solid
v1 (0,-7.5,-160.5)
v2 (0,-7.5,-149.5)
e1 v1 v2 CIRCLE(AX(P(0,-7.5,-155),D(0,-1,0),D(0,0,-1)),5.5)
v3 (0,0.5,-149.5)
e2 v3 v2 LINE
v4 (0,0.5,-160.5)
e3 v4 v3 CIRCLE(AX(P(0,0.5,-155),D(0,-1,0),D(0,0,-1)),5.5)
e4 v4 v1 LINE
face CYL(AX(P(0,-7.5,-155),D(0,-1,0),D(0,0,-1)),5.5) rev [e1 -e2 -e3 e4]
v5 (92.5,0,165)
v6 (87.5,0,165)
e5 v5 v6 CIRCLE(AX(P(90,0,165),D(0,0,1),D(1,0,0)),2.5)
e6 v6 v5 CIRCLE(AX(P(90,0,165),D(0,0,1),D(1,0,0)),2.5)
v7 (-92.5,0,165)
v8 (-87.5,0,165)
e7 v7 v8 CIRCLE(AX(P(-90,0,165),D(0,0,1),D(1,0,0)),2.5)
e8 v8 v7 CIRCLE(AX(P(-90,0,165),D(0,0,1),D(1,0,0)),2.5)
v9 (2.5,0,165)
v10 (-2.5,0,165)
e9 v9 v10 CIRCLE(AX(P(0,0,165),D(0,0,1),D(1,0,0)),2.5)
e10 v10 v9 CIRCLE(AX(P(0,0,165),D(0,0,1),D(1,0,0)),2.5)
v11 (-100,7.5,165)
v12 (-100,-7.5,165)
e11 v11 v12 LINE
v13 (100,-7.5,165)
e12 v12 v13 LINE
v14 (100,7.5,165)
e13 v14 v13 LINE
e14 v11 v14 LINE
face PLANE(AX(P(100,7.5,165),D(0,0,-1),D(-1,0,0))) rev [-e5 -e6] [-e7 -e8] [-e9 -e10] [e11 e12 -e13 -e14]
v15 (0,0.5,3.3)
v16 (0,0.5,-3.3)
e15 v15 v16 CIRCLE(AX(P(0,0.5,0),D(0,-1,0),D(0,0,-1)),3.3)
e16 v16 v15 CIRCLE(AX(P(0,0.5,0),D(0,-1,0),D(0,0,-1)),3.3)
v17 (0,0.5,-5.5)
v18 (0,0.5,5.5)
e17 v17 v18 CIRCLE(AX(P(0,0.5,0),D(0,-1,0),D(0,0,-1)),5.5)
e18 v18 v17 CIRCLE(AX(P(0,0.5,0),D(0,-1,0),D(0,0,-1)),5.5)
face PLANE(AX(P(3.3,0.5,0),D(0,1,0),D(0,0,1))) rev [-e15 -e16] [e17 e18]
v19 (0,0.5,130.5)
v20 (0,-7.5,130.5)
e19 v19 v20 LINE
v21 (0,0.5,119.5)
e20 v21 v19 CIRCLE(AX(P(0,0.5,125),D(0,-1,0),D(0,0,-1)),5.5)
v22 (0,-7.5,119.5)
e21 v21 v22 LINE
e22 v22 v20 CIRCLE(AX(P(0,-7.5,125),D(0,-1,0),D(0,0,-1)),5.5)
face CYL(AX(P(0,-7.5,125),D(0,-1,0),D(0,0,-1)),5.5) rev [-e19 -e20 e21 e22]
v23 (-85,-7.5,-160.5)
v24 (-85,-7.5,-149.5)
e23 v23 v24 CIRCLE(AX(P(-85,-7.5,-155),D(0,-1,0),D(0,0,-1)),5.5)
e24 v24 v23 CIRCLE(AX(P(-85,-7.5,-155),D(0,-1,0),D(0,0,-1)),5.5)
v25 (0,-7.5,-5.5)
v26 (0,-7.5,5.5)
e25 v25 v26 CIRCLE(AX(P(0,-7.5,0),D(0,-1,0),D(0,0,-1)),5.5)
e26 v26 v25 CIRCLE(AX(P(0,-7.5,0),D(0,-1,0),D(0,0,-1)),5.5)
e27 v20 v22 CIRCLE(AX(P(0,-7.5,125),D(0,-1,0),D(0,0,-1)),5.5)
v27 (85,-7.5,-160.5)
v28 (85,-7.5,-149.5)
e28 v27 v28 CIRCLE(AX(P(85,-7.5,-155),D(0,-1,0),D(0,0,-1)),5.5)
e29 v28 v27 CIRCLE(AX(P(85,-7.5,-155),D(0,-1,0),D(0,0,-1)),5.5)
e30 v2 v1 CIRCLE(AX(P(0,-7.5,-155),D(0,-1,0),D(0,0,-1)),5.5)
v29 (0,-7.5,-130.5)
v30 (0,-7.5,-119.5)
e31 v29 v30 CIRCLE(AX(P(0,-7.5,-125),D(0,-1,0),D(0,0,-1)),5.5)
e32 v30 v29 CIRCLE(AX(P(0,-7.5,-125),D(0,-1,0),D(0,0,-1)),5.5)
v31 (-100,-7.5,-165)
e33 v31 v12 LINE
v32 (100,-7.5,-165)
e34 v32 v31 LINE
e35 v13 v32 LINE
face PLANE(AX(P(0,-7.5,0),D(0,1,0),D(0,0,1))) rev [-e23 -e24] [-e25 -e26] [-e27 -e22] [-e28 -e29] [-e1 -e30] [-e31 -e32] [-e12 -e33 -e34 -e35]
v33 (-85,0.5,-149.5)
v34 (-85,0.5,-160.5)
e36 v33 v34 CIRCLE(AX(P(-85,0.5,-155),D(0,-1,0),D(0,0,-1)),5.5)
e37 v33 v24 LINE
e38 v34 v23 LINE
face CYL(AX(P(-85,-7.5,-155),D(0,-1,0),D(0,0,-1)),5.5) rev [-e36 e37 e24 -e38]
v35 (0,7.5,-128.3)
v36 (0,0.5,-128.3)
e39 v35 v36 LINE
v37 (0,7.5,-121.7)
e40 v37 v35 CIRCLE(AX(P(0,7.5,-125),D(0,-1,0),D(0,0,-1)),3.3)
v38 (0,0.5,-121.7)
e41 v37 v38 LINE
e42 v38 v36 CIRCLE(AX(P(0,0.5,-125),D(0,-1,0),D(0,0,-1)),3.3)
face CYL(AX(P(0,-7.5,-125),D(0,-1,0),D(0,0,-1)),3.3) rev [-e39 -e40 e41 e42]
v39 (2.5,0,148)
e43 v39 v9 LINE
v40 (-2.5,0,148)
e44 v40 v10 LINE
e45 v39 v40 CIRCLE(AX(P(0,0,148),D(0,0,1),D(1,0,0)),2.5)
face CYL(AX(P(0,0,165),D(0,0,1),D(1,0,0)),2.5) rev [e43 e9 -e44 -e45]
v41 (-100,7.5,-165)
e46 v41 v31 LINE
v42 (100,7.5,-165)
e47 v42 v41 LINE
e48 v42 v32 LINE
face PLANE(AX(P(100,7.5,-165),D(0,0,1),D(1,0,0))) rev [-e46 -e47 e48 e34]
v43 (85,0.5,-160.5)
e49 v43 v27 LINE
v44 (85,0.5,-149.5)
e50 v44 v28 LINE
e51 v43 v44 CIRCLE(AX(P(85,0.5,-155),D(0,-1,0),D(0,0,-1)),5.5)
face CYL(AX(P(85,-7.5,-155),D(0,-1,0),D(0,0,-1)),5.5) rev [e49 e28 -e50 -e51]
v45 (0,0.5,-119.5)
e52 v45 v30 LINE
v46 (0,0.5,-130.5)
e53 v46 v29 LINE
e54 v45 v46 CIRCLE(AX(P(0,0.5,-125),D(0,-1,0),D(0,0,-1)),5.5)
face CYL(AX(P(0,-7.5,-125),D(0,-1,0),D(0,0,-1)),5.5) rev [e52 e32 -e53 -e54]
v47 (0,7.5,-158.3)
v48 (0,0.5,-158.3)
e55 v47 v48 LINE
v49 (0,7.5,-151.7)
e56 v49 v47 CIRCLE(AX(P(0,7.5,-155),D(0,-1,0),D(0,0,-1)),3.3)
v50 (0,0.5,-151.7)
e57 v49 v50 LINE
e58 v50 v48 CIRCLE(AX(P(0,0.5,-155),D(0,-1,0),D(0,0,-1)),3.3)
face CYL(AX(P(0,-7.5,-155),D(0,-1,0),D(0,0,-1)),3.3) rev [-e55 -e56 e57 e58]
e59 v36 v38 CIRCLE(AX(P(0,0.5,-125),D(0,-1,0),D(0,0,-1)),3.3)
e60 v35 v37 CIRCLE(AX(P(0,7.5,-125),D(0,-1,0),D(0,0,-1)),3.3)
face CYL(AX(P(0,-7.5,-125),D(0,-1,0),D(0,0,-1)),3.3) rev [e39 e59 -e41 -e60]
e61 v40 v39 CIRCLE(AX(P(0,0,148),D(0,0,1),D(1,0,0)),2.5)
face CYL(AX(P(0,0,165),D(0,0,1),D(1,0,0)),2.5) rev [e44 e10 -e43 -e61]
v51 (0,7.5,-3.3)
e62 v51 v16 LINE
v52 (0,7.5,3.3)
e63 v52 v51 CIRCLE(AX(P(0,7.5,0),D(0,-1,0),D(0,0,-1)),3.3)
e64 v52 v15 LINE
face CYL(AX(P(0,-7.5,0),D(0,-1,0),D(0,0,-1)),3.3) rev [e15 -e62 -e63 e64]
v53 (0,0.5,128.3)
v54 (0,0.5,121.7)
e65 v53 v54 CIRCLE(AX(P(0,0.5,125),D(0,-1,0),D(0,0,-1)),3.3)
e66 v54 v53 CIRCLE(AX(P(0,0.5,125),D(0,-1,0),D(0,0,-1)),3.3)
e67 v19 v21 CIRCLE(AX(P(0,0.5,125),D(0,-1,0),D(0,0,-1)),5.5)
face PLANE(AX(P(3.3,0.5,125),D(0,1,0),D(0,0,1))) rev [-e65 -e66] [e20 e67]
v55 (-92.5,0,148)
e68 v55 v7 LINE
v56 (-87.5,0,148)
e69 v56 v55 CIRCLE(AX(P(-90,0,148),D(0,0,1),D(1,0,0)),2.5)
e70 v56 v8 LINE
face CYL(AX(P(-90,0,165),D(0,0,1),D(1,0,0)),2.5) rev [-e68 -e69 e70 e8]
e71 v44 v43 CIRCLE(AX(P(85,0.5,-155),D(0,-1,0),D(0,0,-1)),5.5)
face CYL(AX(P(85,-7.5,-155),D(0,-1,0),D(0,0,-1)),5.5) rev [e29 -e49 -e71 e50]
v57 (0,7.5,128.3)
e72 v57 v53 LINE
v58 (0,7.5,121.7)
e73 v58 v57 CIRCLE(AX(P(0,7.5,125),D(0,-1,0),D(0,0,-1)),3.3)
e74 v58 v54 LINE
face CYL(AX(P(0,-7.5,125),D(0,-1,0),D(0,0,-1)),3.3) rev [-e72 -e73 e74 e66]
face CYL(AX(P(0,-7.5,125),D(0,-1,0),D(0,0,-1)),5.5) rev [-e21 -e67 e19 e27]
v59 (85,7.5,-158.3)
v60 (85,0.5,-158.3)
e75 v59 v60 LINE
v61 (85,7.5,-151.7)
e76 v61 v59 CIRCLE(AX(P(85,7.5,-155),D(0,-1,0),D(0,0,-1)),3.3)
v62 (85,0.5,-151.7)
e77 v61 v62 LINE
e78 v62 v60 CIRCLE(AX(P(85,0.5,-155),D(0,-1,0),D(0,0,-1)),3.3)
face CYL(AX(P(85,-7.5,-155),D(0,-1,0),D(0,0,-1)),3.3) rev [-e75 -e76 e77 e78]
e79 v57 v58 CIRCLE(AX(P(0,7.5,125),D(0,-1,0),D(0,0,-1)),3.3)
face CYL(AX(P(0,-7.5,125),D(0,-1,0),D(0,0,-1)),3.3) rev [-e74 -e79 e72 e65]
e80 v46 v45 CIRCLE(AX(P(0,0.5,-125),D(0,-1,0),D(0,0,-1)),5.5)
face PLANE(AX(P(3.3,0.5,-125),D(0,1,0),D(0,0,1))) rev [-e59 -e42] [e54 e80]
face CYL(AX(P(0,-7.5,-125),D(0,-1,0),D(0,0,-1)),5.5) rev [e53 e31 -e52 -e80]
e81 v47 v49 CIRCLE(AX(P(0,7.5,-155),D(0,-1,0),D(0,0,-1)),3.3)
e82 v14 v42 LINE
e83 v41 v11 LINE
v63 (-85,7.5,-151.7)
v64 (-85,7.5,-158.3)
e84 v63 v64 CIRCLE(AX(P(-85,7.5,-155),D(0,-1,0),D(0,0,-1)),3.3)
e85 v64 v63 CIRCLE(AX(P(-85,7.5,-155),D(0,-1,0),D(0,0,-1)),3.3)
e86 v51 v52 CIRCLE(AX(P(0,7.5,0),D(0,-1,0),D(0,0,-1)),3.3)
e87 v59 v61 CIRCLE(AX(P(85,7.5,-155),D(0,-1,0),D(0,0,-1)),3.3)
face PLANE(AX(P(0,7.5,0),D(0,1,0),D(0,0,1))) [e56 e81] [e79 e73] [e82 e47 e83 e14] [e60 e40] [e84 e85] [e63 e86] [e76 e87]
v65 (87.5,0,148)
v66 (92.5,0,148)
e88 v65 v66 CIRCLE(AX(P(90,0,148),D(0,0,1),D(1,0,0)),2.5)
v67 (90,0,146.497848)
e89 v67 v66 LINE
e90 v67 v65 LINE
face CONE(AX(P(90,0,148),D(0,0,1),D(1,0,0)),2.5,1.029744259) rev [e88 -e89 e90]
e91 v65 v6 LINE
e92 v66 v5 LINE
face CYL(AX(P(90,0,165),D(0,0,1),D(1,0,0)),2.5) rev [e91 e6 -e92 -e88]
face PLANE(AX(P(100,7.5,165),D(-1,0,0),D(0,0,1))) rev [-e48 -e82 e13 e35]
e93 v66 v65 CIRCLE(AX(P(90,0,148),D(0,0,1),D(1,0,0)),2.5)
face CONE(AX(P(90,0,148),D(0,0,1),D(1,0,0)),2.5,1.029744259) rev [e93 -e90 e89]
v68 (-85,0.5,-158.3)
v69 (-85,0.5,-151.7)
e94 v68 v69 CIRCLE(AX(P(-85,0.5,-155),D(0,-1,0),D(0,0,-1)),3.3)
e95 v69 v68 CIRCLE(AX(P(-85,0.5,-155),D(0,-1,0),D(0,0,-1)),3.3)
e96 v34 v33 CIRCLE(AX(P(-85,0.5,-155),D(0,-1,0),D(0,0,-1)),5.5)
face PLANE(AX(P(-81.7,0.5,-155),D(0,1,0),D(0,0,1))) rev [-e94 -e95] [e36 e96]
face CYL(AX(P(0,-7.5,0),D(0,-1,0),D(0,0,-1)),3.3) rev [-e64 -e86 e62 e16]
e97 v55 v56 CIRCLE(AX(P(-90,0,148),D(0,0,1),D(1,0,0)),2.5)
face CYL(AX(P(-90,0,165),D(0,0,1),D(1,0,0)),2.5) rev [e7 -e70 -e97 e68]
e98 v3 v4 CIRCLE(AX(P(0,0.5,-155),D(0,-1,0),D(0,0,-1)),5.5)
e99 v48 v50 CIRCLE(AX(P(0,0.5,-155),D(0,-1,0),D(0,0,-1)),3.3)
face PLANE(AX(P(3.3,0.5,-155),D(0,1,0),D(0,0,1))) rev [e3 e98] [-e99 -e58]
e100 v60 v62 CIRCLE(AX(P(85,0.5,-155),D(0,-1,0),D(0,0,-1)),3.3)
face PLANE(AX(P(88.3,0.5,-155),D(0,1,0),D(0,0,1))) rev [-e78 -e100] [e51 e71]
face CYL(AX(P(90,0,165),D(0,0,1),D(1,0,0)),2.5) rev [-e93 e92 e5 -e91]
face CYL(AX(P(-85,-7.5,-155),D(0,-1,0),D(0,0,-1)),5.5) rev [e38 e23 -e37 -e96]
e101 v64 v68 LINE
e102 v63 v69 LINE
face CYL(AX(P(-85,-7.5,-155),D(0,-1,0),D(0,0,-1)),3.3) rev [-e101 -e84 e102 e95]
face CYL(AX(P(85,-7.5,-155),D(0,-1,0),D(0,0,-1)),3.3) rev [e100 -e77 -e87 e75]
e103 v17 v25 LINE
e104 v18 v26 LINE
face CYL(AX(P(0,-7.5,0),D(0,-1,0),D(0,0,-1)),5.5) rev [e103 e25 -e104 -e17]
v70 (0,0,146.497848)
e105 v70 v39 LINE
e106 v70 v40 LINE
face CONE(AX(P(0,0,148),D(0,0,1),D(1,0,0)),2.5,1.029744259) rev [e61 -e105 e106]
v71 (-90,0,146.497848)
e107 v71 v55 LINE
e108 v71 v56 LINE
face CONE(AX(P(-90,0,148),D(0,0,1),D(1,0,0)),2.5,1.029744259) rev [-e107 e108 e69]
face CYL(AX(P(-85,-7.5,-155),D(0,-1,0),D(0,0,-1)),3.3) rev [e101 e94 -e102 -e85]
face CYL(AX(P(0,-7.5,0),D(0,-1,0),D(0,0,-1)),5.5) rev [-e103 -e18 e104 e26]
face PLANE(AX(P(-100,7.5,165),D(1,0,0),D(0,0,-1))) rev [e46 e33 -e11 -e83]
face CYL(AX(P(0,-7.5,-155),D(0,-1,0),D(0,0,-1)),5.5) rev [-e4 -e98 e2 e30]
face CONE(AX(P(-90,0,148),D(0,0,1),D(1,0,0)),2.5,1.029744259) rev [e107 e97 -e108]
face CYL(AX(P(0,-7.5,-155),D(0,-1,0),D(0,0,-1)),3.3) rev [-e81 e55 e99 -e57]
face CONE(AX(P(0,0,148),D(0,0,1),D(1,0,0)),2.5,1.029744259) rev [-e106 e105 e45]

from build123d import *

# Parameters (mm, degrees)
SKETCH_1_W                   = 200
SKETCH_1_H                   = 330
EXTRUDE_1_DEPTH              = 7.5
HOLE_WIZARD_M6_1_D           = 6.6
HOLE_WIZARD_M6_1_CBORE_D     = 11
HOLE_WIZARD_M6_1_CBORE_DEPTH = 8
HOLE_WIZARD_M6_2_D           = 6.6
HOLE_WIZARD_M6_2_CBORE_D     = 11
HOLE_WIZARD_M6_2_CBORE_DEPTH = 8
HOLE_WIZARD_M6_1_2_D         = 5
HOLE_WIZARD_M6_1_2_DEPTH     = 17
HOLE_WIZARD_M6_1_2_TIP       = 1.502151548


with BuildPart() as part:
    # 草图1 → 凸台-拉伸1 (new, symmetric)
    with BuildSketch(Plane(origin=(0, 0, 0), x_dir=(1, 0, 0), z_dir=(0, 1, 0))):
        Rectangle(SKETCH_1_W, SKETCH_1_H)
    extrude(amount=EXTRUDE_1_DEPTH, both=True)

    # Hole Wizard M6 _1 (through all)
    with Locations(Plane(origin=(0, -7.5, 0), x_dir=(-1, 0, 0), z_dir=(0, -1, 0))):
        with Locations((0, 0), (0, -125), (0, 125)):
            CounterBoreHole(HOLE_WIZARD_M6_1_D / 2, HOLE_WIZARD_M6_1_CBORE_D / 2, HOLE_WIZARD_M6_1_CBORE_DEPTH)

    # M6 六角凹头螺钉的柱形沉头孔2 (through all)
    with Locations(Plane(origin=(0, -7.5, 0), x_dir=(-1, 0, 0), z_dir=(0, -1, 0))):
        with Locations((85, 155), (0, 155), (-85, 155)):
            CounterBoreHole(HOLE_WIZARD_M6_2_D / 2, HOLE_WIZARD_M6_2_CBORE_D / 2, HOLE_WIZARD_M6_2_CBORE_DEPTH)

    # Hole Wizard M6 _1 2
    with Locations(Plane.XY.offset(165)):
        with Locations((0, 0), (-90, 0), (90, 0)):
            Hole(HOLE_WIZARD_M6_1_2_D / 2, depth=HOLE_WIZARD_M6_1_2_DEPTH)
            with Locations((0, 0, -(HOLE_WIZARD_M6_1_2_DEPTH + HOLE_WIZARD_M6_1_2_TIP / 2))):  # 118° drill point
                Cone(0, HOLE_WIZARD_M6_1_2_D / 2, HOLE_WIZARD_M6_1_2_TIP, mode=Mode.SUBTRACT)


solid = part.part
